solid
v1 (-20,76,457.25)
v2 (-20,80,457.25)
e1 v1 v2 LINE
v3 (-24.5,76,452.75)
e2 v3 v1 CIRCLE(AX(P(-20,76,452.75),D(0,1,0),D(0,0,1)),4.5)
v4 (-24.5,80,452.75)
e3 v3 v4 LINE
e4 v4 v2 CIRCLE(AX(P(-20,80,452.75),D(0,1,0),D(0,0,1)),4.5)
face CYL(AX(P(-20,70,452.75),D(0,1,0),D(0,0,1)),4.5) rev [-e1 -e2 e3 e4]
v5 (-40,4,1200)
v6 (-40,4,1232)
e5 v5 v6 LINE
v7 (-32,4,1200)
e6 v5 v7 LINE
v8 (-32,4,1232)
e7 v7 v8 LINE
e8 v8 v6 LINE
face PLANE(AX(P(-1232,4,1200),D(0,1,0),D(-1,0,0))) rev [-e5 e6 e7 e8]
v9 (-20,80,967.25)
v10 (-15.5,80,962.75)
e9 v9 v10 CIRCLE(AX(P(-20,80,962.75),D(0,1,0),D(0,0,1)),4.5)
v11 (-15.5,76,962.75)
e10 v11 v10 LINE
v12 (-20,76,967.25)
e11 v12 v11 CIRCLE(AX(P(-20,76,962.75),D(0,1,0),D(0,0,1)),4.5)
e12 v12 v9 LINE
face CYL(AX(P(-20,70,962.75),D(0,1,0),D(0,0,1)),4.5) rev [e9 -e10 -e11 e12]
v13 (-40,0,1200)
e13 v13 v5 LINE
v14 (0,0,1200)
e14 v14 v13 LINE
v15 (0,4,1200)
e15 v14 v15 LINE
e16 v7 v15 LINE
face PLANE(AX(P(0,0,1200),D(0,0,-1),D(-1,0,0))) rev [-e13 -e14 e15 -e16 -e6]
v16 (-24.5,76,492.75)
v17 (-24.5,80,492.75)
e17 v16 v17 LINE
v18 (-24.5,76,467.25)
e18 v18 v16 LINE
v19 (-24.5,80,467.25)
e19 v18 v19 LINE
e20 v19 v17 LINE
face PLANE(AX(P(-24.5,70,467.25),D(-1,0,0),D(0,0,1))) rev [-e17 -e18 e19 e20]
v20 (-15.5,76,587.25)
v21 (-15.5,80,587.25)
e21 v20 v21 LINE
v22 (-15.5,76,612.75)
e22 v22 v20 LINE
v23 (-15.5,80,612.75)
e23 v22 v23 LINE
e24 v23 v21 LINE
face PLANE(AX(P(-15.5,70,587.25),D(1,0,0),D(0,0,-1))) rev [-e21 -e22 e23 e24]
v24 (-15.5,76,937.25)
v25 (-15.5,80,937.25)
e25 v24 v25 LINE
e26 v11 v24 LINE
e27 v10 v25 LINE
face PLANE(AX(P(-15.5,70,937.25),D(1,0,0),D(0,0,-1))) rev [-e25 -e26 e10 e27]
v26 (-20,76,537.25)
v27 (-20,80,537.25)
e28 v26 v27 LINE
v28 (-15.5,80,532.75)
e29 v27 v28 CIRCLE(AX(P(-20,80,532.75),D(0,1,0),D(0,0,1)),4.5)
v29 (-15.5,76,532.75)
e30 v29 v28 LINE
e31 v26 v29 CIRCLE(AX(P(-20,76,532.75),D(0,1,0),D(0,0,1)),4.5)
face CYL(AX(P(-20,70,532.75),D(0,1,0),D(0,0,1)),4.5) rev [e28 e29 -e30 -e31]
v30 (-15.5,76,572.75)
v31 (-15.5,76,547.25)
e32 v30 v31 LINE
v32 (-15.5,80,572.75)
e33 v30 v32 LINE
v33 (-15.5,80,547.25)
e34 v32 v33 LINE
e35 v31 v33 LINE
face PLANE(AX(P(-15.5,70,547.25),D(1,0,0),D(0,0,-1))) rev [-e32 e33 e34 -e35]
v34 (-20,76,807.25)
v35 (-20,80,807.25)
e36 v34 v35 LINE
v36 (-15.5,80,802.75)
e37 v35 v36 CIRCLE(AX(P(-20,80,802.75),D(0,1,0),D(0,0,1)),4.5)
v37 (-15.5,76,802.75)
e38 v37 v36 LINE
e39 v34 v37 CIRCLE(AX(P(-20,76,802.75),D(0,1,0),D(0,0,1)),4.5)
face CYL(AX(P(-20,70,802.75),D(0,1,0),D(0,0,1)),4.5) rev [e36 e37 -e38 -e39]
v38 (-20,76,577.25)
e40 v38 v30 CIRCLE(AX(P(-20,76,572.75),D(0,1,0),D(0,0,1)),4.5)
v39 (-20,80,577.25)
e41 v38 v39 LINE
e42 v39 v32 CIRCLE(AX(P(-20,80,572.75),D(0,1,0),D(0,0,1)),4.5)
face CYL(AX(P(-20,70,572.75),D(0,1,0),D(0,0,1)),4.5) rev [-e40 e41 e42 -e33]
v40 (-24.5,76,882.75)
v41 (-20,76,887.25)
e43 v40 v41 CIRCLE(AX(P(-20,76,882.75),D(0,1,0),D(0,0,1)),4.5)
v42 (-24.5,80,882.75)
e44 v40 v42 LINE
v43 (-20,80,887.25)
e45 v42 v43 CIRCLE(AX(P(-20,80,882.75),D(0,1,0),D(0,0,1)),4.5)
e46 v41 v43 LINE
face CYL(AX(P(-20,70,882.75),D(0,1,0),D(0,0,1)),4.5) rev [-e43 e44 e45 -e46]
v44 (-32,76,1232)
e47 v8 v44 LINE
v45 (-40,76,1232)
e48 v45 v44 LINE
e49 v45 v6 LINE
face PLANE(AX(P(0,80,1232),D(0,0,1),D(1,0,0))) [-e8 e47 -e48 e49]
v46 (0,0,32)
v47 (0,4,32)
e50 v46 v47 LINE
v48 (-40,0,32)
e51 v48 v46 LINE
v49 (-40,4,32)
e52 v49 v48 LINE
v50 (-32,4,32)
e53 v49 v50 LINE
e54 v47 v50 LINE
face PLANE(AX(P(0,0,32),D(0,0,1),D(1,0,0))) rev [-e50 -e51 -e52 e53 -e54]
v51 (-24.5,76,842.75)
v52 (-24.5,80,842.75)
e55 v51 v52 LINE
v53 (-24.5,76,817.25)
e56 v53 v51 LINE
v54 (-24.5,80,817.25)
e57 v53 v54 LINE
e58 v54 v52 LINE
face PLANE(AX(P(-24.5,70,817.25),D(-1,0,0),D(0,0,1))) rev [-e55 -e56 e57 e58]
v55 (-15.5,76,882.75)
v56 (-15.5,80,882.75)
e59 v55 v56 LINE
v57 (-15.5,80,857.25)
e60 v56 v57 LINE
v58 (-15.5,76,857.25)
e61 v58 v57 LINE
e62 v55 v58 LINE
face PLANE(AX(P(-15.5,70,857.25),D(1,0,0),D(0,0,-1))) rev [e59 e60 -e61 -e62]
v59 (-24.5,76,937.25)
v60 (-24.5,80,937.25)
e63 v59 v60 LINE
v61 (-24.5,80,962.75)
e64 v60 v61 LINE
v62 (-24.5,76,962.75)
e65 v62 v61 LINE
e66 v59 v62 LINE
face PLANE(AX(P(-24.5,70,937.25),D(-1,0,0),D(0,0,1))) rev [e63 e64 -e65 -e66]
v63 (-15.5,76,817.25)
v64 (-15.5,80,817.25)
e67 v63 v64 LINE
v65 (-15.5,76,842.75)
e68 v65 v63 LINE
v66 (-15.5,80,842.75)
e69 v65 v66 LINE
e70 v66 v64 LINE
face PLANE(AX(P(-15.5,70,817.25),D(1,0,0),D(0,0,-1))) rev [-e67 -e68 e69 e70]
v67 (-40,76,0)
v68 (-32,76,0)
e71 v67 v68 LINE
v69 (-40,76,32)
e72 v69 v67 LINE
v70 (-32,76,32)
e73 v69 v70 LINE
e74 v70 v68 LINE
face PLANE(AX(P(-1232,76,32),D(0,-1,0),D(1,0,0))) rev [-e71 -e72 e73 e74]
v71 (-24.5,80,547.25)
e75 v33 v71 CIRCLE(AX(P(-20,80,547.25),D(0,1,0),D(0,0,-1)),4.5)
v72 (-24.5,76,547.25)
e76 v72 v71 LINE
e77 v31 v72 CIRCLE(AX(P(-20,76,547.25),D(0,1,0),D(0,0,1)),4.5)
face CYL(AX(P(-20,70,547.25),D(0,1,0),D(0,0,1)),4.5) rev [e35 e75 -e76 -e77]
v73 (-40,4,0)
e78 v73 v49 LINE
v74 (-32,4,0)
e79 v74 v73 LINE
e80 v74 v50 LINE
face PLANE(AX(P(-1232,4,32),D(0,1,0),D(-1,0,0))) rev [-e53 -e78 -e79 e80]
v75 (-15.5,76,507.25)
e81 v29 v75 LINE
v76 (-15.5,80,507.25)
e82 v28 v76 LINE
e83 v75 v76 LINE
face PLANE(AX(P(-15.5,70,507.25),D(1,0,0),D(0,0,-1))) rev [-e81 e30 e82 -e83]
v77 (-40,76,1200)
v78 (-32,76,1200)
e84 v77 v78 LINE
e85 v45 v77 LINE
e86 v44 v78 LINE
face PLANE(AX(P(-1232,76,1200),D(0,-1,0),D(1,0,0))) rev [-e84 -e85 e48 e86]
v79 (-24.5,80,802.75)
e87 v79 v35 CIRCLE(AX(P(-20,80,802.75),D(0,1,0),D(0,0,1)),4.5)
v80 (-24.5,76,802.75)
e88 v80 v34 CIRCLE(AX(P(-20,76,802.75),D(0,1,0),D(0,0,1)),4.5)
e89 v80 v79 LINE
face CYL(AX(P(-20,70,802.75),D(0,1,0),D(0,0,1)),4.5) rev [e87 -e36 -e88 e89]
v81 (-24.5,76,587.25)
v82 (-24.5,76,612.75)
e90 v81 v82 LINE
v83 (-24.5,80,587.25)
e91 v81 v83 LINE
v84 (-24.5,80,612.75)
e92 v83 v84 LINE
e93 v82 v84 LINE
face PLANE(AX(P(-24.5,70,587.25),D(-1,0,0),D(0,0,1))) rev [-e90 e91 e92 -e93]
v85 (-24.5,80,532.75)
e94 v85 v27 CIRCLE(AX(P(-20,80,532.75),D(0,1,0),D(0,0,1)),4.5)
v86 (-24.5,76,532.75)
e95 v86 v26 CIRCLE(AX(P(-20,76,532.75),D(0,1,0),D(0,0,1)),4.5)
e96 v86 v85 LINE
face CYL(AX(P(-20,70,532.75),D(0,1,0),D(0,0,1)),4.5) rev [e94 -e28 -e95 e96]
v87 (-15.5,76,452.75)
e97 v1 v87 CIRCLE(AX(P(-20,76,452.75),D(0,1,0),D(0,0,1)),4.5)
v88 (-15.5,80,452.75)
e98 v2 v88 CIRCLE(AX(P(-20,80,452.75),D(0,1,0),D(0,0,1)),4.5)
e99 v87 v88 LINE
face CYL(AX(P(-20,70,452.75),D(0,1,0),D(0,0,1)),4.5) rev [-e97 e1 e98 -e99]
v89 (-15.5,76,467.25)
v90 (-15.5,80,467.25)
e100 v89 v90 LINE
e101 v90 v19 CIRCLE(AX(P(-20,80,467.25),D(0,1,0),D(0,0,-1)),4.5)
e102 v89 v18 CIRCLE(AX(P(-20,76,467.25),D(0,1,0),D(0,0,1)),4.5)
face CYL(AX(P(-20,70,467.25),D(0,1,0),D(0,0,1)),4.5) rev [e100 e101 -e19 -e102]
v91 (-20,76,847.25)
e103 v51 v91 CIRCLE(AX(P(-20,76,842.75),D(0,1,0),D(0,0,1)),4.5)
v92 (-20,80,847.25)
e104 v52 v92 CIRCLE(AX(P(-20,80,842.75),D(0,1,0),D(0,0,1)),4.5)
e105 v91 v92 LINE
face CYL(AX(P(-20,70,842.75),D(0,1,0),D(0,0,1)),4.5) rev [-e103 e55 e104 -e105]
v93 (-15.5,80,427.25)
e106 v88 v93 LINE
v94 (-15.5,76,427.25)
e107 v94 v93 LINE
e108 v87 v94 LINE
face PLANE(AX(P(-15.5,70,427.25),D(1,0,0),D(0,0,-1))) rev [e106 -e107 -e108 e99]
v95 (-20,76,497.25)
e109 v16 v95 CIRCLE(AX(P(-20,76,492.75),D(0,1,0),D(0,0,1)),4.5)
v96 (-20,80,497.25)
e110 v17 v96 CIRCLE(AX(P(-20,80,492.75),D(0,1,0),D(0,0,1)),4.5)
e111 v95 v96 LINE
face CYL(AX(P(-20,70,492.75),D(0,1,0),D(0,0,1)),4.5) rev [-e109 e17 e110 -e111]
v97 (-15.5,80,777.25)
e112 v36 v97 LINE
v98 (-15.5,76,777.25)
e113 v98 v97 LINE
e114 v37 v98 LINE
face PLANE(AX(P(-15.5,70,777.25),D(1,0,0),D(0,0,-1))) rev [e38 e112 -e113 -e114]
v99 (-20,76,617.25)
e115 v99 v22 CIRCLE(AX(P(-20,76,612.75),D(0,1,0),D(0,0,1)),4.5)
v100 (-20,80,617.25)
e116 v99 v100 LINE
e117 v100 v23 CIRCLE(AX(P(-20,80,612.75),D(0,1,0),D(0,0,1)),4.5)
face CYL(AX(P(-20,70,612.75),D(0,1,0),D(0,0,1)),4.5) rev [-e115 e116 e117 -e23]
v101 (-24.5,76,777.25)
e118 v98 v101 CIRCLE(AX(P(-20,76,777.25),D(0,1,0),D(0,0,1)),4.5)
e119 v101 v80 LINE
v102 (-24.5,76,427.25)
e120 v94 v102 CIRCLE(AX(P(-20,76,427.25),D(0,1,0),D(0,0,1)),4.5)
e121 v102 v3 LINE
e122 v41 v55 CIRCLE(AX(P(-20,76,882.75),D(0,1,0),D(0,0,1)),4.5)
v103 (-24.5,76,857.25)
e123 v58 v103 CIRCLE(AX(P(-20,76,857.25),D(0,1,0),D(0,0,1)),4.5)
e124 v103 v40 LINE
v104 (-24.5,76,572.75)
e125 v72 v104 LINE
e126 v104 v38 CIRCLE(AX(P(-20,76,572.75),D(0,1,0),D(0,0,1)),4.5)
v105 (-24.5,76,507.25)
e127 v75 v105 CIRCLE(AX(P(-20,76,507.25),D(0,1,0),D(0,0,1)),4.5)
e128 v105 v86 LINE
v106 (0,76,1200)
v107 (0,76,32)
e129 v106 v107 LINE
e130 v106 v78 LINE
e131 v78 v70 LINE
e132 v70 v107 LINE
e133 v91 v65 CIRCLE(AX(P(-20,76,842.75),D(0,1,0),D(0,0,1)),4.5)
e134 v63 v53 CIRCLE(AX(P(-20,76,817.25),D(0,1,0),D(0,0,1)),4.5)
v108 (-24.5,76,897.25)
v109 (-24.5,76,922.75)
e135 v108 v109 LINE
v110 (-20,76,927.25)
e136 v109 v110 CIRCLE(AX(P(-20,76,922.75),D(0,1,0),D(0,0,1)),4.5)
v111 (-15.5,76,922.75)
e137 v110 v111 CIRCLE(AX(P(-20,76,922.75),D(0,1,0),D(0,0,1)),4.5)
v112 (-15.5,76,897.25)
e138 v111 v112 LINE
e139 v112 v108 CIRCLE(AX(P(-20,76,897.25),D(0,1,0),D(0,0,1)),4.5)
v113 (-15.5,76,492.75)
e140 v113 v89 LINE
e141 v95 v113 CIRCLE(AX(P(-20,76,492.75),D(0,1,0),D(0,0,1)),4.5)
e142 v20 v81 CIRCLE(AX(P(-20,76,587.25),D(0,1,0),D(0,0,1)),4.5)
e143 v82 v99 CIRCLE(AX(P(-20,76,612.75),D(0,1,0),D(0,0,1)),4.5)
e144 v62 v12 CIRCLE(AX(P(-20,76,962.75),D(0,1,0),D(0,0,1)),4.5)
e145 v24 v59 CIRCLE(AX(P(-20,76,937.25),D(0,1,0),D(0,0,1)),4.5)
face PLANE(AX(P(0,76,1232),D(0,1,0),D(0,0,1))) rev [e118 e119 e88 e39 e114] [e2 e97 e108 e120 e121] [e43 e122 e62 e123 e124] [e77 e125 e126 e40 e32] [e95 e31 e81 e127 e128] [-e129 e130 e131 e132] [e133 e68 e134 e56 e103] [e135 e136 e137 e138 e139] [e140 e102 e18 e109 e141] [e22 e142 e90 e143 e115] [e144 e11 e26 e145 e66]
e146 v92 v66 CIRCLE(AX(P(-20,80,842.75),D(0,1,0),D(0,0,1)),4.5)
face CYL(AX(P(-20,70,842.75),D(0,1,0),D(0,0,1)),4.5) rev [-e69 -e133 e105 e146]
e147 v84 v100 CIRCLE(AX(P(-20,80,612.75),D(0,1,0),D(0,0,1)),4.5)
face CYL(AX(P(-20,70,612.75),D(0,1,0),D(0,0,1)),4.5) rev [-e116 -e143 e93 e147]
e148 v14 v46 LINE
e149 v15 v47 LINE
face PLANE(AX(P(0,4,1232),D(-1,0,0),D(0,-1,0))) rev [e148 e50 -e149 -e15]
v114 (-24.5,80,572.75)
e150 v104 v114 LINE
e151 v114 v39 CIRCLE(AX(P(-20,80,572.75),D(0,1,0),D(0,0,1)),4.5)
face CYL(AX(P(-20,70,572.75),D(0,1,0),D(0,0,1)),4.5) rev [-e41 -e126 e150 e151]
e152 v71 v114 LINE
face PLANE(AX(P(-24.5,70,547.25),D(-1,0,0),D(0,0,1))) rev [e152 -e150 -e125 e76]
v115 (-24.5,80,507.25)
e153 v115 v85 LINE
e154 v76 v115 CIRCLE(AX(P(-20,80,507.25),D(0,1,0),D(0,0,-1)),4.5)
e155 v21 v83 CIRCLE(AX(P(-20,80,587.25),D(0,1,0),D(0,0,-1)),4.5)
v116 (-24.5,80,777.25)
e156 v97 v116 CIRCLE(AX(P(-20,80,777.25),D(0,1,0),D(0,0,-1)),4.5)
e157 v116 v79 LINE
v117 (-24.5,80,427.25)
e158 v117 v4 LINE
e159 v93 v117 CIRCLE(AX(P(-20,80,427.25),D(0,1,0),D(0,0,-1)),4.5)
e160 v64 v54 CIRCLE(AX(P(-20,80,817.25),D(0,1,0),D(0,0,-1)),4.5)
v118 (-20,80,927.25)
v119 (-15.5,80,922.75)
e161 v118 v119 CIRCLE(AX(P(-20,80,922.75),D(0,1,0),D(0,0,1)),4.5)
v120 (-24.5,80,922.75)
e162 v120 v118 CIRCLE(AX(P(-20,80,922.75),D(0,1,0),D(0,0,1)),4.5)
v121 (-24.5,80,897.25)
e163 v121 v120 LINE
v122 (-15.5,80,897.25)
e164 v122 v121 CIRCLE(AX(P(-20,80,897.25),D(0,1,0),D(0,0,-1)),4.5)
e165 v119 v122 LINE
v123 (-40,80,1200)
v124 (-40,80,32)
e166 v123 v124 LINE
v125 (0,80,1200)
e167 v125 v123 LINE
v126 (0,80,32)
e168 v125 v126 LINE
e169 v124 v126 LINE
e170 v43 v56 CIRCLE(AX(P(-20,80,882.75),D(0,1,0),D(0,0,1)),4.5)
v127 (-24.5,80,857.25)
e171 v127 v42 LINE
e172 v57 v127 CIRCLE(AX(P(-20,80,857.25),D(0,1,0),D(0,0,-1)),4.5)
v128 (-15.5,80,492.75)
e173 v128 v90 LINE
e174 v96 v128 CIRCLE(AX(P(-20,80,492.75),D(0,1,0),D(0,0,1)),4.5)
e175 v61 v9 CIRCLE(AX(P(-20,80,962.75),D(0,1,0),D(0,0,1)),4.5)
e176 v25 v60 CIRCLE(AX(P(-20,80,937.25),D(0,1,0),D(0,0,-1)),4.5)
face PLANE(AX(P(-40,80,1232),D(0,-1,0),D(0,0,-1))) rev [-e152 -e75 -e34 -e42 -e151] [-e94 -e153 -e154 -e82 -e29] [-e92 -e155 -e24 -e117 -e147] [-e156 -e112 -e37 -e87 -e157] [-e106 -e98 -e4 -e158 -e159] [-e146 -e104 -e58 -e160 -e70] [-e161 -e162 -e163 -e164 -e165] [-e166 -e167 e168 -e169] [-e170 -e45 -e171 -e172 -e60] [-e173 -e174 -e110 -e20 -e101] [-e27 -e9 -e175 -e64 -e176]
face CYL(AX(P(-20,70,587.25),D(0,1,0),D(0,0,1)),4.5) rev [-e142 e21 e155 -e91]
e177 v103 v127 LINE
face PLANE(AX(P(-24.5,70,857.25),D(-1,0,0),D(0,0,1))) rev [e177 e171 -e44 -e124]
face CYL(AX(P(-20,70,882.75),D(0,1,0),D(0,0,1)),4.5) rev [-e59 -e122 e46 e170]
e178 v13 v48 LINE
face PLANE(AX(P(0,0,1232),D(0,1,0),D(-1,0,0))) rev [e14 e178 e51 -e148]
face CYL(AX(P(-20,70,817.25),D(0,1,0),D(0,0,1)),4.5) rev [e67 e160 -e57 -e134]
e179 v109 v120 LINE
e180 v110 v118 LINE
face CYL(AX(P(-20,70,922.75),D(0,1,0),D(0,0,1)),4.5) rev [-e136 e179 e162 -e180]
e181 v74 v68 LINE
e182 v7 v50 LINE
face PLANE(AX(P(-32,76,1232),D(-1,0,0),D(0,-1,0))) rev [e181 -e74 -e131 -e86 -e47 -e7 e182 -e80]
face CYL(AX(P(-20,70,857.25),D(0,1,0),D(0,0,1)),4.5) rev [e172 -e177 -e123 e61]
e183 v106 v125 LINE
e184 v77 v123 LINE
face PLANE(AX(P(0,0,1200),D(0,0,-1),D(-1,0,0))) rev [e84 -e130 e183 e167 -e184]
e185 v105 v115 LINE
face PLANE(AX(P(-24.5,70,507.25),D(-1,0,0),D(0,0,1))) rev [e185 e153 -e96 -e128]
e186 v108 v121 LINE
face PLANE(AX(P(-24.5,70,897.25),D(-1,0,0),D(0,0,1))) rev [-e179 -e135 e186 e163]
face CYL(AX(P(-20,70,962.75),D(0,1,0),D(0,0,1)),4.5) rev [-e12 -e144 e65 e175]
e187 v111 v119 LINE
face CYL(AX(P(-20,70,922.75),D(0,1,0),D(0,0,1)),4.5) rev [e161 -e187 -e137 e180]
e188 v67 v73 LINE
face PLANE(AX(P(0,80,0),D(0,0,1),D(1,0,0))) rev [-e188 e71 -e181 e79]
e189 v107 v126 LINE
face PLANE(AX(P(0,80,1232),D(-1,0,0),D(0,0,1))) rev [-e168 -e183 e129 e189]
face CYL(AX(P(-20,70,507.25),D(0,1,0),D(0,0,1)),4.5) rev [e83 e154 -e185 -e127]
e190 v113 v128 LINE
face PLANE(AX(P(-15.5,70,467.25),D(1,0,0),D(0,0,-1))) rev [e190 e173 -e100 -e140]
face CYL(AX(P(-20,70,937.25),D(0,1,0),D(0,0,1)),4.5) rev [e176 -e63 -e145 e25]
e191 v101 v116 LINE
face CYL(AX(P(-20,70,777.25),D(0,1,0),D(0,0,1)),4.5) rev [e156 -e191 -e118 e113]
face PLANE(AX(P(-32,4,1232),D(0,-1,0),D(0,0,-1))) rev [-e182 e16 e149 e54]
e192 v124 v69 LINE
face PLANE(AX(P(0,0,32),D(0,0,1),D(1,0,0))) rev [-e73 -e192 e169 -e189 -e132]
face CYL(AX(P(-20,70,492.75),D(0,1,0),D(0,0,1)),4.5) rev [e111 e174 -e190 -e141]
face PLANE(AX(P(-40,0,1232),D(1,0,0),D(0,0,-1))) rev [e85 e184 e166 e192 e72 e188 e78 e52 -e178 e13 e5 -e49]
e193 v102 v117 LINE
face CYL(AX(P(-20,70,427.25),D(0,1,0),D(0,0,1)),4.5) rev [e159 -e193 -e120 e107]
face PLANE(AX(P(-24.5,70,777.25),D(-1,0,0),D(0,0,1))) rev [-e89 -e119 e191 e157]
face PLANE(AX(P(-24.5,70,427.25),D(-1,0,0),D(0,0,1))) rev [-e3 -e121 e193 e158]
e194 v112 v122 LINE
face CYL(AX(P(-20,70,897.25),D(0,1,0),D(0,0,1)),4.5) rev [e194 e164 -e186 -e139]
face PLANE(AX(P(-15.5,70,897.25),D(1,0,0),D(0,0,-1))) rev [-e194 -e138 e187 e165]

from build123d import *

# Parameters (mm, degrees)
EXTRUDE1_DEPTH         = 1232
SKETCH2_W              = 32
SKETCH2_H              = 32
CUT_EXTRUDE1_DEPTH     = 1236.242486316
SKETCH3_W              = 32
SKETCH3_H              = 4
CUT_EXTRUDE2_DEPTH     = 1200
CUT_EXTRUDE3_DEPTH     = 10
LPATTERN1_COUNT        = 5
LPATTERN1_PITCH        = 40
LPATTERN2_COUNT        = 2
LPATTERN2_PITCH        = 350
LPATTERN2_COPY_1_DEPTH = 10
LPATTERN2_COPY_2_DEPTH = 10
LPATTERN2_COPY_3_DEPTH = 10
LPATTERN2_COPY_4_DEPTH = 10


with BuildPart() as part:
    # Sketch1 → Extrude1 (new body)
    with BuildSketch(Plane.XY):
        Polygon((0, 0), (-40, 0), (-40, 80), (0, 80), (0, 76), (-32, 76), (-32, 4), (0, 4), align=None)
    extrude(amount=EXTRUDE1_DEPTH)

    # Sketch2 → Cut-Extrude1 (cut, through all)
    with BuildSketch(Plane(origin=(0, 80, 0), x_dir=(1, 0, 0), z_dir=(0, 1, 0))):
        with Locations((-16, -16)):
            Rectangle(SKETCH2_W, SKETCH2_H)
        with Locations((-16, -1216)):
            Rectangle(SKETCH2_W, SKETCH2_H)
    extrude(amount=-CUT_EXTRUDE1_DEPTH, mode=Mode.SUBTRACT)

    # Sketch3 → Cut-Extrude2 (cut)
    with BuildSketch(Plane(origin=(-32, 0, 0), x_dir=(0, 0, -1), z_dir=(1, 0, 0))):
        with Locations((-1216, 78)):
            Rectangle(SKETCH3_W, SKETCH3_H)
        with Locations((-1216, 2)):
            Rectangle(SKETCH3_W, SKETCH3_H)
        with Locations((-16, 78)):
            Rectangle(SKETCH3_W, SKETCH3_H)
        with Locations((-16, 2)):
            Rectangle(SKETCH3_W, SKETCH3_H)
    extrude(amount=-CUT_EXTRUDE2_DEPTH, mode=Mode.SUBTRACT)

    # Sketch4 → Cut-Extrude3 (cut)
    with BuildSketch(Plane(origin=(0, 80, 0), x_dir=(1, 0, 0), z_dir=(0, 1, 0))):
        with BuildLine():
            Line((-24.5, -937.25), (-24.5, -962.75))
            ThreePointArc((-24.5, -962.75), (-20, -967.25), (-15.5, -962.75))
            Line((-15.5, -962.75), (-15.5, -937.25))
            ThreePointArc((-15.5, -937.25), (-20, -932.75), (-24.5, -937.25))
        make_face()
    cut_extrude3 = extrude(amount=-CUT_EXTRUDE3_DEPTH, mode=Mode.SUBTRACT)

    # LPattern1: Cut-Extrude3 ×5
    with Locations(*[(0, 0, -i * LPATTERN1_PITCH) for i in range(1, LPATTERN1_COUNT)]):
        add(cut_extrude3, mode=Mode.SUBTRACT)

    # LPattern2: Cut-Extrude3 ×2
    with Locations(*[(0, 0, -i * LPATTERN2_PITCH) for i in range(1, LPATTERN2_COUNT)]):
        add(cut_extrude3, mode=Mode.SUBTRACT)

    # LPattern2 copy 1 sketch → LPattern2 copy 1 (cut)
    with BuildSketch(Plane(origin=(0, 80, -390), x_dir=(1, 0, 0), z_dir=(0, 1, 0))):
        with BuildLine():
            Line((-24.5, -937.25), (-24.5, -962.75))
            ThreePointArc((-24.5, -962.75), (-20, -967.25), (-15.5, -962.75))
            Line((-15.5, -962.75), (-15.5, -937.25))
            ThreePointArc((-15.5, -937.25), (-20, -932.75), (-24.5, -937.25))
        make_face()
    extrude(amount=-LPATTERN2_COPY_1_DEPTH, mode=Mode.SUBTRACT)

    # LPattern2 copy 2 sketch → LPattern2 copy 2 (cut)
    with BuildSketch(Plane(origin=(0, 80, -430), x_dir=(1, 0, 0), z_dir=(0, 1, 0))):
        with BuildLine():
            Line((-24.5, -937.25), (-24.5, -962.75))
            ThreePointArc((-24.5, -962.75), (-20, -967.25), (-15.5, -962.75))
            Line((-15.5, -962.75), (-15.5, -937.25))
            ThreePointArc((-15.5, -937.25), (-20, -932.75), (-24.5, -937.25))
        make_face()
    extrude(amount=-LPATTERN2_COPY_2_DEPTH, mode=Mode.SUBTRACT)

    # LPattern2 copy 3 sketch → LPattern2 copy 3 (cut)
    with BuildSketch(Plane(origin=(0, 80, -470), x_dir=(1, 0, 0), z_dir=(0, 1, 0))):
        with BuildLine():
            Line((-24.5, -937.25), (-24.5, -962.75))
            ThreePointArc((-24.5, -962.75), (-20, -967.25), (-15.5, -962.75))
            Line((-15.5, -962.75), (-15.5, -937.25))
            ThreePointArc((-15.5, -937.25), (-20, -932.75), (-24.5, -937.25))
        make_face()
    extrude(amount=-LPATTERN2_COPY_3_DEPTH, mode=Mode.SUBTRACT)

    # LPattern2 copy 4 sketch → LPattern2 copy 4 (cut)
    with BuildSketch(Plane(origin=(0, 80, -510), x_dir=(1, 0, 0), z_dir=(0, 1, 0))):
        with BuildLine():
            Line((-24.5, -937.25), (-24.5, -962.75))
            ThreePointArc((-24.5, -962.75), (-20, -967.25), (-15.5, -962.75))
            Line((-15.5, -962.75), (-15.5, -937.25))
            ThreePointArc((-15.5, -937.25), (-20, -932.75), (-24.5, -937.25))
        make_face()
    extrude(amount=-LPATTERN2_COPY_4_DEPTH, mode=Mode.SUBTRACT)


solid = part.part
